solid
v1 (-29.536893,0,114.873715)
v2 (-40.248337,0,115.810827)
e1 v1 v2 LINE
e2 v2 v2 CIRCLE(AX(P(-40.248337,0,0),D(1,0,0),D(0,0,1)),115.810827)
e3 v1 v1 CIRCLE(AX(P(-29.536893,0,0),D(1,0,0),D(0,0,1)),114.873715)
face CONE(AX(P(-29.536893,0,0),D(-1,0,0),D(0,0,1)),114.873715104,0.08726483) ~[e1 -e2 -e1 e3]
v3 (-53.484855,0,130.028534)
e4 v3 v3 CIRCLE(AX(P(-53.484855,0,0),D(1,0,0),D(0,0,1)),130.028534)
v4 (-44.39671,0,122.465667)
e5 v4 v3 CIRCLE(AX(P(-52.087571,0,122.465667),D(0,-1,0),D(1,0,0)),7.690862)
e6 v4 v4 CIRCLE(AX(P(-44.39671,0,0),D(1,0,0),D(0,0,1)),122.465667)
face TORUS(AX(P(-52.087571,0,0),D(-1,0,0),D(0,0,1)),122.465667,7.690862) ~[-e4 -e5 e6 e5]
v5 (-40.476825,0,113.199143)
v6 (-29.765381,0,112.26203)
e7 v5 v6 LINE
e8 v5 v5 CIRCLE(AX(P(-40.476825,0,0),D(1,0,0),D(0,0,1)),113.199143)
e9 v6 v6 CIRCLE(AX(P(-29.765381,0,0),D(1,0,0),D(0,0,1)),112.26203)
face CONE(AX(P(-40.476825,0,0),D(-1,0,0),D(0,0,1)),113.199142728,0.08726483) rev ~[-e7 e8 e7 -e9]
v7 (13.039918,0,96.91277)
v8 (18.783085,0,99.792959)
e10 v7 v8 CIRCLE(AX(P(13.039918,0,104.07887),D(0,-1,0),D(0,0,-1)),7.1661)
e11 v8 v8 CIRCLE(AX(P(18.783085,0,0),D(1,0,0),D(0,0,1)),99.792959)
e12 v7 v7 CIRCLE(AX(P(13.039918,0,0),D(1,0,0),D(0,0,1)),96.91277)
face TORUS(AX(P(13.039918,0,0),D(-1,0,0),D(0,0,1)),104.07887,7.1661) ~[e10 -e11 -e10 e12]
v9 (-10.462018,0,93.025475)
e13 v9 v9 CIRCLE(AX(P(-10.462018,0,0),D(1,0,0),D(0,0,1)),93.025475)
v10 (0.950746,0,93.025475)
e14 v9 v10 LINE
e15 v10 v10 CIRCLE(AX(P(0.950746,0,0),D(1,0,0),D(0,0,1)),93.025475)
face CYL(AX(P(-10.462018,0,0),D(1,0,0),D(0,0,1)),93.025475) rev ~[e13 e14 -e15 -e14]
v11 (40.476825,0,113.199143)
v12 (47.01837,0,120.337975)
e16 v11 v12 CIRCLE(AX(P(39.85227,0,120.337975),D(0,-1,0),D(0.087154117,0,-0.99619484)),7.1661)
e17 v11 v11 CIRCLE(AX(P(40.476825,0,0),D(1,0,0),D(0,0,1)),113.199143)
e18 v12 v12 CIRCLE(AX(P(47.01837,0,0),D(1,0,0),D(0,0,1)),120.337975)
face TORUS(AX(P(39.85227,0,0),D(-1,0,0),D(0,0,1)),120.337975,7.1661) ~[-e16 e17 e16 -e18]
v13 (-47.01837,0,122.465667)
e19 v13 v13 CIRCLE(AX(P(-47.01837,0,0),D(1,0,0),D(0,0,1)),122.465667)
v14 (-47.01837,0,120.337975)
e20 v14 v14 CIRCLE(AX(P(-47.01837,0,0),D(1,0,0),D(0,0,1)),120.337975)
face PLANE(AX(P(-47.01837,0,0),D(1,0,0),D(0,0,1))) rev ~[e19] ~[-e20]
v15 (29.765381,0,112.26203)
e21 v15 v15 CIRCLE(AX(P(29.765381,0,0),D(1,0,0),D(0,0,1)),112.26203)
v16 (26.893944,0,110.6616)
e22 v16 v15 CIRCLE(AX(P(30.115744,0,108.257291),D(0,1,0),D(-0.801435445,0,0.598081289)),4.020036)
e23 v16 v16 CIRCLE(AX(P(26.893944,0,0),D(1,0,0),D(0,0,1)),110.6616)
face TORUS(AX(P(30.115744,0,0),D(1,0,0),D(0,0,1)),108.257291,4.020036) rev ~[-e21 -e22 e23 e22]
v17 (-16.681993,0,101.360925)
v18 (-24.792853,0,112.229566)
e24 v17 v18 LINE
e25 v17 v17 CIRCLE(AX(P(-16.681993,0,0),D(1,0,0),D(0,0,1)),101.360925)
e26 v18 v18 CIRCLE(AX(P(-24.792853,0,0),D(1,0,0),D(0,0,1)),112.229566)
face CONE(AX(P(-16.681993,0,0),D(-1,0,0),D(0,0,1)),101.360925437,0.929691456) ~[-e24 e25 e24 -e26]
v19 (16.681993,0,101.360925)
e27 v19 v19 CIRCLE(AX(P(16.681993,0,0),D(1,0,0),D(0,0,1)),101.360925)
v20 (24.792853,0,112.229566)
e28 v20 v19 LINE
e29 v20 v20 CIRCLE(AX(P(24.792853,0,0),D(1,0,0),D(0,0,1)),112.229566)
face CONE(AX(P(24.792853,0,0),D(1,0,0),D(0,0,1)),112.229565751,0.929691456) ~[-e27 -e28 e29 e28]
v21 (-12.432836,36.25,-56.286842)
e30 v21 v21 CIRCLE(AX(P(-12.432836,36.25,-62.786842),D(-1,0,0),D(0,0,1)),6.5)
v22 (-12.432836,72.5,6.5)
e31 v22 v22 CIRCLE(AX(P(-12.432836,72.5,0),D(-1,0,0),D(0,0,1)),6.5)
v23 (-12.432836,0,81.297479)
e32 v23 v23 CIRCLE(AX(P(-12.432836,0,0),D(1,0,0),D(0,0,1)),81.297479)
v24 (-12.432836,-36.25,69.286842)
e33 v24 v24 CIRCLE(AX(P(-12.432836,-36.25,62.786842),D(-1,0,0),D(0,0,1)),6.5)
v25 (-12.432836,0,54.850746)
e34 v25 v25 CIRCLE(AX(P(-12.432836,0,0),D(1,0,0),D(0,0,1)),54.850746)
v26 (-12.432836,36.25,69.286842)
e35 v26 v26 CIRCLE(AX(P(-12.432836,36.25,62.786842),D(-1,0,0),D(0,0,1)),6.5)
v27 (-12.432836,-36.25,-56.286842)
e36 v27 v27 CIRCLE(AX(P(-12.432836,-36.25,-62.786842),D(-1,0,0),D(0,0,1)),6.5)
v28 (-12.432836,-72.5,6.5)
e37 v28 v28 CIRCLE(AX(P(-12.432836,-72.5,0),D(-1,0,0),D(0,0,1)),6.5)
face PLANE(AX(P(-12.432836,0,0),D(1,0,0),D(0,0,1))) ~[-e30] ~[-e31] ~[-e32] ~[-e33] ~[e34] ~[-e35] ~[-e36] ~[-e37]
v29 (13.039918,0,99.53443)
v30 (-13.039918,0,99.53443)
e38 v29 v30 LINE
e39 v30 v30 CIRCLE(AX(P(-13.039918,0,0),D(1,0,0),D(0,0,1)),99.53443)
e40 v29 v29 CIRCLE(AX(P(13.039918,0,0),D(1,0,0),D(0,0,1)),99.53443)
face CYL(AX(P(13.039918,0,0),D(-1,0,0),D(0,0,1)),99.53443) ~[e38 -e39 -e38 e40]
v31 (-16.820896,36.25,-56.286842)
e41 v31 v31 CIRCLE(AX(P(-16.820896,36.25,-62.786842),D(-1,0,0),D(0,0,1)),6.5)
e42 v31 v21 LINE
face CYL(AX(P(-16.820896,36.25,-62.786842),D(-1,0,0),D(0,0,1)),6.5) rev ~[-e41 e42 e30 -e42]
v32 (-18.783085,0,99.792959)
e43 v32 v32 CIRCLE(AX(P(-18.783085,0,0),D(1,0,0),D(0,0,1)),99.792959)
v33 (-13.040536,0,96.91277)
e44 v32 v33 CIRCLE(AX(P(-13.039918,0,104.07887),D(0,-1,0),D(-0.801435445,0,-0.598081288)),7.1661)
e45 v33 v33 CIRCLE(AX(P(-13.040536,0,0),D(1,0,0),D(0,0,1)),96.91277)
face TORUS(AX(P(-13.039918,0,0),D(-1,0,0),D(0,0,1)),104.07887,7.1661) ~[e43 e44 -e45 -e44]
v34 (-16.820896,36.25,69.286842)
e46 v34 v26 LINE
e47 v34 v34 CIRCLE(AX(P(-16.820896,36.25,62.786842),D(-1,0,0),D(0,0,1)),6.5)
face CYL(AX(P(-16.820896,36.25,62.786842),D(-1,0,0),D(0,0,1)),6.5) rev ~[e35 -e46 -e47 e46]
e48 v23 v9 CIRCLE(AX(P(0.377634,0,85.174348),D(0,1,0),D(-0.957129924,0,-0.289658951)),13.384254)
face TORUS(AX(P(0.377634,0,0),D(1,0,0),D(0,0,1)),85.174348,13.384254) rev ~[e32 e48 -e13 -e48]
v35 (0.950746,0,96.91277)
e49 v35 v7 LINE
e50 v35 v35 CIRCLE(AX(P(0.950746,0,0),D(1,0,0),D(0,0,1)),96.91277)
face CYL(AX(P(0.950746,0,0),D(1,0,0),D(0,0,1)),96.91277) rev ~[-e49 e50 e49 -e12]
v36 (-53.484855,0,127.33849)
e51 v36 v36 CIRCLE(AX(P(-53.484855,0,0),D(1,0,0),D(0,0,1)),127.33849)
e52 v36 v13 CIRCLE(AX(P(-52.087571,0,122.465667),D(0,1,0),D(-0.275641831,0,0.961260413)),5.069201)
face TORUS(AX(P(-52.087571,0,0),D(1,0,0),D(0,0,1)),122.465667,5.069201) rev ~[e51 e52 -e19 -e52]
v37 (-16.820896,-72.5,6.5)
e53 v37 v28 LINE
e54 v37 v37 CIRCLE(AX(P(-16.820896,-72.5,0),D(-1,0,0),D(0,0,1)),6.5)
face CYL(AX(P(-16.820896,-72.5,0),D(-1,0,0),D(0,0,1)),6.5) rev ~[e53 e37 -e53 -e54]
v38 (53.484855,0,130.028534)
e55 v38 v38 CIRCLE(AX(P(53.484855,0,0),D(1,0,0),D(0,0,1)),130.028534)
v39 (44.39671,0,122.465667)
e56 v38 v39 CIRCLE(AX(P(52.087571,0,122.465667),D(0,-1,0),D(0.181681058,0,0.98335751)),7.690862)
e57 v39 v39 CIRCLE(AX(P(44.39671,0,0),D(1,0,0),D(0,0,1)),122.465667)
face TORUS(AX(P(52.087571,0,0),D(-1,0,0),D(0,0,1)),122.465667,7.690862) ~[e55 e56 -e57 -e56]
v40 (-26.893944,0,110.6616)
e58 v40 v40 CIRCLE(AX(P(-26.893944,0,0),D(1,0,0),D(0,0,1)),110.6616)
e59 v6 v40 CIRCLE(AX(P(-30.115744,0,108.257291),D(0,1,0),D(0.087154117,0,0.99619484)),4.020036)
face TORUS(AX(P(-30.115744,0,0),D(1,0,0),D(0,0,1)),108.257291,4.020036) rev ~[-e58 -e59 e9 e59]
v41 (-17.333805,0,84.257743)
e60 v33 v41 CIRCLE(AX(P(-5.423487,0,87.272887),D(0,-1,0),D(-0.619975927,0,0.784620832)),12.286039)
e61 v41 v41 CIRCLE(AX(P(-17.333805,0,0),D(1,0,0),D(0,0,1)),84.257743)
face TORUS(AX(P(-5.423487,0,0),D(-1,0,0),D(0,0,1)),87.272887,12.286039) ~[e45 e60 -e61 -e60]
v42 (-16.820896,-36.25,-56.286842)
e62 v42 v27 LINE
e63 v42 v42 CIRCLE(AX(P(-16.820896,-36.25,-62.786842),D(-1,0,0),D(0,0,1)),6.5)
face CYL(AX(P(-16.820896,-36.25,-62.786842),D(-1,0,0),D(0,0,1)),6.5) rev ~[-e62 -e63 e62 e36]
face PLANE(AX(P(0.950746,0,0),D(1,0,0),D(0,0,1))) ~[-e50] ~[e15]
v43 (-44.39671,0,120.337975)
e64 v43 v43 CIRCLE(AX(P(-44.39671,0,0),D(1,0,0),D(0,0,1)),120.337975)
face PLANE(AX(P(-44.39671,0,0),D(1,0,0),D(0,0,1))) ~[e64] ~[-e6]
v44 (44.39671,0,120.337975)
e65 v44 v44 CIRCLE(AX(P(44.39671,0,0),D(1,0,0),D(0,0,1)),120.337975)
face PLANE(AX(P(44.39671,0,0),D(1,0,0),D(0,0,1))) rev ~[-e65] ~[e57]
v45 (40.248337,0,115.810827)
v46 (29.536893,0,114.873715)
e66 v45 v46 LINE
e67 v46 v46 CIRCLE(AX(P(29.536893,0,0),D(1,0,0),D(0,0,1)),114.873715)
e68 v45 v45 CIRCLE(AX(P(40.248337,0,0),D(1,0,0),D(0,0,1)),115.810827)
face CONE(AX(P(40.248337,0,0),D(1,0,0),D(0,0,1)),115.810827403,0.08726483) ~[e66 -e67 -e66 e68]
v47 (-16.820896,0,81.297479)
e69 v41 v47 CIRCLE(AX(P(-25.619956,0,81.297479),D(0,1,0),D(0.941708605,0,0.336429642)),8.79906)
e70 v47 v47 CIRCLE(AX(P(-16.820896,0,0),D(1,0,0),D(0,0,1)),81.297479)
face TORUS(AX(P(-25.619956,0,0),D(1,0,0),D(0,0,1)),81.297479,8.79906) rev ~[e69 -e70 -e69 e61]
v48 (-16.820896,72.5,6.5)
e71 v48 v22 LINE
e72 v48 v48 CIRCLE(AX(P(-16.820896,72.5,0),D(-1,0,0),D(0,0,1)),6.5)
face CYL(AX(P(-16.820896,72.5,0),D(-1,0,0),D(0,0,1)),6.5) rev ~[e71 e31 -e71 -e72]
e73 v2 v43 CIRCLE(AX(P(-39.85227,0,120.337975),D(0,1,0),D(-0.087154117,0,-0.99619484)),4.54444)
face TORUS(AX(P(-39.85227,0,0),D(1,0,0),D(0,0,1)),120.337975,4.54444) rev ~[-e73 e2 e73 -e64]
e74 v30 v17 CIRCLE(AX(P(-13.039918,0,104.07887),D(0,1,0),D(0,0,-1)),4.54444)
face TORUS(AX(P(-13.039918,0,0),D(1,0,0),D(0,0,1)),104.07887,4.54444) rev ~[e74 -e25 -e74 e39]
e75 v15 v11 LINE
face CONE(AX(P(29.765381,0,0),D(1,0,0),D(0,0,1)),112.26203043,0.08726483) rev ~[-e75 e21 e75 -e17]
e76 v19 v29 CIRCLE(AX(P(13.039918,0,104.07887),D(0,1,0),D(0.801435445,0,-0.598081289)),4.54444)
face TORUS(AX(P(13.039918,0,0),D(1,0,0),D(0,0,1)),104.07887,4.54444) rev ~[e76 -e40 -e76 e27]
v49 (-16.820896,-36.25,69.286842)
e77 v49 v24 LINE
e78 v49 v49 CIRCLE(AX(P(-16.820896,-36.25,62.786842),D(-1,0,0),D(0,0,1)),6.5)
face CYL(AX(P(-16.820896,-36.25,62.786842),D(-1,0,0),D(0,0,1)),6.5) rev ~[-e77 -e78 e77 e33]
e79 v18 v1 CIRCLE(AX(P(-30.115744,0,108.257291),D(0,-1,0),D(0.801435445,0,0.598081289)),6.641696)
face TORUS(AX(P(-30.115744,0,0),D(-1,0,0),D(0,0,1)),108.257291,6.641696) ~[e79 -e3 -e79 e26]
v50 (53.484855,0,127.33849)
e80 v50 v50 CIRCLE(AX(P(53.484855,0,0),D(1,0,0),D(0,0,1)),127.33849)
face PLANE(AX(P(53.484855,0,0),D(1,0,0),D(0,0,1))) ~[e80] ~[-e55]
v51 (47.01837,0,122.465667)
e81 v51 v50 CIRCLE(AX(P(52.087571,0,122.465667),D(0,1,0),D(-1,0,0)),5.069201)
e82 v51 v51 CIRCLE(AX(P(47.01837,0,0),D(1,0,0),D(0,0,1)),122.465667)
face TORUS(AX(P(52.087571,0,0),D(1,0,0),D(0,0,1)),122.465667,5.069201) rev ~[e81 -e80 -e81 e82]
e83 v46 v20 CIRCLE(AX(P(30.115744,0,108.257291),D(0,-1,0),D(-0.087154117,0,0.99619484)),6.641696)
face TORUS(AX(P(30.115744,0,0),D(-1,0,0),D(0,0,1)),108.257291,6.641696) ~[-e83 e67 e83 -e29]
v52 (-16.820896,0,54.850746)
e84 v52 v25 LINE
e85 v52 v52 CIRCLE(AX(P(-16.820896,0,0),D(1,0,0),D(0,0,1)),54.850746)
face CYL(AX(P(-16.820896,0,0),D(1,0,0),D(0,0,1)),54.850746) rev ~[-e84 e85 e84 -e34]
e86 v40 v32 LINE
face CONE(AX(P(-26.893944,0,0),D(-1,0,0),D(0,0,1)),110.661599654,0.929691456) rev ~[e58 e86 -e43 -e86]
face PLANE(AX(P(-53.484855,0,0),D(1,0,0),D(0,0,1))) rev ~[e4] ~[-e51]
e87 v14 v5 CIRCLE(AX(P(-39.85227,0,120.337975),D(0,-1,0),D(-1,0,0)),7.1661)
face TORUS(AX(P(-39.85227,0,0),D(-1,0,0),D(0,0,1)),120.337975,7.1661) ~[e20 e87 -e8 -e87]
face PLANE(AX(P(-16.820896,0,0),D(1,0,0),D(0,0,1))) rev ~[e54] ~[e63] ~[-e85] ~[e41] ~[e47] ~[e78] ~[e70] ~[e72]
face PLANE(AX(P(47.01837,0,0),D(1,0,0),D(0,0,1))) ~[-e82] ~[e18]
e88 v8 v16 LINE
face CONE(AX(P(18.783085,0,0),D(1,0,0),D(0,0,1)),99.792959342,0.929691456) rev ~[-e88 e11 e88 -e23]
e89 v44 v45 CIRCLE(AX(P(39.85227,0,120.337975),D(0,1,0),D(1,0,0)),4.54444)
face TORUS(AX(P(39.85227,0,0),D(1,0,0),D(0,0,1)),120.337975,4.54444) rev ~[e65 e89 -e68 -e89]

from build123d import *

# Parameters (mm, degrees)
SCALE_1_SCALE       = 0.731343284
CUT_EXTRUDE_2_REACH = 199.039
SKETCH_4_R          = 6.5


with BuildPart() as part:
    # 草图2 → 旋转1 (revolve)
    with BuildSketch(Plane.XY, mode=Mode.PRIVATE) as revolve_1_sk:
        with BuildLine():
            Line((55.03343969, 158.353580236), (40.387179575, 157.072222603))
            ThreePointArc((40.387179575, 157.072222603), (36.757353818, 155.957845796), (33.90043136, 153.456753082))
            Line((33.90043136, 153.456753082), (22.81007227, 138.595551029))
            ThreePointArc((22.81007227, 138.595551029), (20.615656314, 136.757442651), (17.830091986, 136.098098151))
            Line((17.830091986, 136.098098151), (-17.830091986, 136.098098151))
            ThreePointArc((-17.830091986, 136.098098151), (-20.615656314, 136.757442651), (-22.81007227, 138.595551029))
            Line((-22.81007227, 138.595551029), (-33.90043136, 153.456753082))
            ThreePointArc((-33.90043136, 153.456753082), (-36.757353818, 155.957845796), (-40.387179575, 157.072222603))
            Line((-40.387179575, 157.072222603), (-55.03343969, 158.353580236))
            ThreePointArc((-55.03343969, 158.353580236), (-59.073188734, 160.345757851), (-60.705705036, 164.543761485))
            Line((-60.705705036, 164.543761485), (-60.705705036, 167.453055254))
            ThreePointArc((-60.705705036, 167.453055254), (-64.495112644, 175.536358254), (-73.132352941, 177.794117647))
            Line((-73.132352941, 177.794117647), (-73.132352941, 174.115893968))
            ThreePointArc((-73.132352941, 174.115893968), (-67.050399463, 172.988692483), (-64.290424508, 167.453055254))
            Line((-64.290424508, 167.453055254), (-64.290424508, 164.543761485))
            ThreePointArc((-64.290424508, 164.543761485), (-61.716119183, 157.923954321), (-55.345862749, 154.782501193))
            Line((-55.345862749, 154.782501193), (-40.699602634, 153.501143561))
            ThreePointArc((-40.699602634, 153.501143561), (-38.50256908, 152.826641973), (-36.773352605, 151.312799441))
            Line((-36.773352605, 151.312799441), (-25.682993515, 136.451597389))
            ThreePointArc((-25.682993515, 136.451597389), (-22.223009506, 133.553284489), (-17.830936762, 132.513378715))
            ThreePointArc((-17.830936762, 132.513378715), (-23.324500539, 124.729410215), (-23.701325224, 115.209567162))
            ThreePointArc((-23.701325224, 115.209567162), (-23.176627808, 113.215866858), (-23, 111.161858362))
            Line((-23, 111.161858362), (-23, 75))
            Line((-23, 75), (-17, 75))
            Line((-17, 75), (-17, 111.161858362))
            ThreePointArc((-17, 111.161858362), (-17.531511204, 119.495717118), (-14.305208, 127.198098151))
            Line((-14.305208, 127.198098151), (1.3, 127.198098151))
            Line((1.3, 127.198098151), (1.3, 132.513378678))
            Line((1.3, 132.513378678), (17.830091986, 132.513378678))
            ThreePointArc((17.830091986, 132.513378678), (22.222631941, 133.553095131), (25.682993515, 136.451597389))
            Line((25.682993515, 136.451597389), (36.773352605, 151.312799441))
            ThreePointArc((36.773352605, 151.312799441), (38.50256908, 152.826641973), (40.699602634, 153.501143561))
            Line((40.699602634, 153.501143561), (55.345862749, 154.782501193))
            ThreePointArc((55.345862749, 154.782501193), (61.716119183, 157.923954321), (64.290424508, 164.543761485))
            Line((64.290424508, 164.543761485), (64.290424508, 167.453055254))
            ThreePointArc((64.290424508, 167.453055254), (67.050399463, 172.988692483), (73.132352941, 174.115893968))
            Line((73.132352941, 174.115893968), (73.132352941, 177.794117647))
            ThreePointArc((73.132352941, 177.794117647), (64.495112644, 175.536358254), (60.705705036, 167.453055254))
            Line((60.705705036, 167.453055254), (60.705705036, 164.543761485))
            ThreePointArc((60.705705036, 164.543761485), (59.073188734, 160.345757851), (55.03343969, 158.353580236))
        make_face()
    revolve(revolve_1_sk.sketch.rotate(Axis((0, 0, 0), (1, 0, 0)), 90), axis=Axis((0, 0, 0), (1, 0, 0)))


with BuildPart() as part_1:
    # 缩放比例1: scaled about (0, 0, 0)
    add(part.part.scale(SCALE_1_SCALE))

    # 草图4 → 切除-拉伸2 (cut, up to next)
    with BuildSketch(Plane.ZY.offset(16.820895522), mode=Mode.PRIVATE) as cut_extrude_2_sk1:
        with Locations((0, 72.5)):
            Circle(SKETCH_4_R)
    cut_extrude_2_tool1 = extrude(cut_extrude_2_sk1.sketch, amount=-CUT_EXTRUDE_2_REACH, mode=Mode.PRIVATE) & part_1.part
    # 草图4 → 切除-拉伸2 (cut, up to next)
    with BuildSketch(Plane.ZY.offset(16.820895522), mode=Mode.PRIVATE) as cut_extrude_2_sk2:
        with Locations((62.786841774, 36.25)):
            Circle(SKETCH_4_R)
    cut_extrude_2_tool2 = extrude(cut_extrude_2_sk2.sketch, amount=-CUT_EXTRUDE_2_REACH, mode=Mode.PRIVATE) & part_1.part
    # 草图4 → 切除-拉伸2 (cut, up to next)
    with BuildSketch(Plane.ZY.offset(16.820895522), mode=Mode.PRIVATE) as cut_extrude_2_sk3:
        with Locations((62.786841774, -36.25)):
            Circle(SKETCH_4_R)
    cut_extrude_2_tool3 = extrude(cut_extrude_2_sk3.sketch, amount=-CUT_EXTRUDE_2_REACH, mode=Mode.PRIVATE) & part_1.part
    # 草图4 → 切除-拉伸2 (cut, up to next)
    with BuildSketch(Plane.ZY.offset(16.820895522), mode=Mode.PRIVATE) as cut_extrude_2_sk4:
        with Locations((0, -72.5)):
            Circle(SKETCH_4_R)
    cut_extrude_2_tool4 = extrude(cut_extrude_2_sk4.sketch, amount=-CUT_EXTRUDE_2_REACH, mode=Mode.PRIVATE) & part_1.part
    # 草图4 → 切除-拉伸2 (cut, up to next)
    with BuildSketch(Plane.ZY.offset(16.820895522), mode=Mode.PRIVATE) as cut_extrude_2_sk5:
        with Locations((-62.786841774, -36.25)):
            Circle(SKETCH_4_R)
    cut_extrude_2_tool5 = extrude(cut_extrude_2_sk5.sketch, amount=-CUT_EXTRUDE_2_REACH, mode=Mode.PRIVATE) & part_1.part
    # 草图4 → 切除-拉伸2 (cut, up to next)
    with BuildSketch(Plane.ZY.offset(16.820895522), mode=Mode.PRIVATE) as cut_extrude_2_sk6:
        with Locations((-62.786841774, 36.25)):
            Circle(SKETCH_4_R)
    cut_extrude_2_tool6 = extrude(cut_extrude_2_sk6.sketch, amount=-CUT_EXTRUDE_2_REACH, mode=Mode.PRIVATE) & part_1.part
    add(cut_extrude_2_tool1.solids().sort_by_distance((-16.820896, 72.5, 0))[0], mode=Mode.SUBTRACT)
    add(cut_extrude_2_tool2.solids().sort_by_distance((-16.820896, 36.25, 62.786842))[0], mode=Mode.SUBTRACT)
    add(cut_extrude_2_tool3.solids().sort_by_distance((-16.820896, -36.25, 62.786842))[0], mode=Mode.SUBTRACT)
    add(cut_extrude_2_tool4.solids().sort_by_distance((-16.820896, -72.5, 0))[0], mode=Mode.SUBTRACT)
    add(cut_extrude_2_tool5.solids().sort_by_distance((-16.820896, -36.25, -62.786842))[0], mode=Mode.SUBTRACT)
    add(cut_extrude_2_tool6.solids().sort_by_distance((-16.820896, 36.25, -62.786842))[0], mode=Mode.SUBTRACT)


solid = part_1.part
